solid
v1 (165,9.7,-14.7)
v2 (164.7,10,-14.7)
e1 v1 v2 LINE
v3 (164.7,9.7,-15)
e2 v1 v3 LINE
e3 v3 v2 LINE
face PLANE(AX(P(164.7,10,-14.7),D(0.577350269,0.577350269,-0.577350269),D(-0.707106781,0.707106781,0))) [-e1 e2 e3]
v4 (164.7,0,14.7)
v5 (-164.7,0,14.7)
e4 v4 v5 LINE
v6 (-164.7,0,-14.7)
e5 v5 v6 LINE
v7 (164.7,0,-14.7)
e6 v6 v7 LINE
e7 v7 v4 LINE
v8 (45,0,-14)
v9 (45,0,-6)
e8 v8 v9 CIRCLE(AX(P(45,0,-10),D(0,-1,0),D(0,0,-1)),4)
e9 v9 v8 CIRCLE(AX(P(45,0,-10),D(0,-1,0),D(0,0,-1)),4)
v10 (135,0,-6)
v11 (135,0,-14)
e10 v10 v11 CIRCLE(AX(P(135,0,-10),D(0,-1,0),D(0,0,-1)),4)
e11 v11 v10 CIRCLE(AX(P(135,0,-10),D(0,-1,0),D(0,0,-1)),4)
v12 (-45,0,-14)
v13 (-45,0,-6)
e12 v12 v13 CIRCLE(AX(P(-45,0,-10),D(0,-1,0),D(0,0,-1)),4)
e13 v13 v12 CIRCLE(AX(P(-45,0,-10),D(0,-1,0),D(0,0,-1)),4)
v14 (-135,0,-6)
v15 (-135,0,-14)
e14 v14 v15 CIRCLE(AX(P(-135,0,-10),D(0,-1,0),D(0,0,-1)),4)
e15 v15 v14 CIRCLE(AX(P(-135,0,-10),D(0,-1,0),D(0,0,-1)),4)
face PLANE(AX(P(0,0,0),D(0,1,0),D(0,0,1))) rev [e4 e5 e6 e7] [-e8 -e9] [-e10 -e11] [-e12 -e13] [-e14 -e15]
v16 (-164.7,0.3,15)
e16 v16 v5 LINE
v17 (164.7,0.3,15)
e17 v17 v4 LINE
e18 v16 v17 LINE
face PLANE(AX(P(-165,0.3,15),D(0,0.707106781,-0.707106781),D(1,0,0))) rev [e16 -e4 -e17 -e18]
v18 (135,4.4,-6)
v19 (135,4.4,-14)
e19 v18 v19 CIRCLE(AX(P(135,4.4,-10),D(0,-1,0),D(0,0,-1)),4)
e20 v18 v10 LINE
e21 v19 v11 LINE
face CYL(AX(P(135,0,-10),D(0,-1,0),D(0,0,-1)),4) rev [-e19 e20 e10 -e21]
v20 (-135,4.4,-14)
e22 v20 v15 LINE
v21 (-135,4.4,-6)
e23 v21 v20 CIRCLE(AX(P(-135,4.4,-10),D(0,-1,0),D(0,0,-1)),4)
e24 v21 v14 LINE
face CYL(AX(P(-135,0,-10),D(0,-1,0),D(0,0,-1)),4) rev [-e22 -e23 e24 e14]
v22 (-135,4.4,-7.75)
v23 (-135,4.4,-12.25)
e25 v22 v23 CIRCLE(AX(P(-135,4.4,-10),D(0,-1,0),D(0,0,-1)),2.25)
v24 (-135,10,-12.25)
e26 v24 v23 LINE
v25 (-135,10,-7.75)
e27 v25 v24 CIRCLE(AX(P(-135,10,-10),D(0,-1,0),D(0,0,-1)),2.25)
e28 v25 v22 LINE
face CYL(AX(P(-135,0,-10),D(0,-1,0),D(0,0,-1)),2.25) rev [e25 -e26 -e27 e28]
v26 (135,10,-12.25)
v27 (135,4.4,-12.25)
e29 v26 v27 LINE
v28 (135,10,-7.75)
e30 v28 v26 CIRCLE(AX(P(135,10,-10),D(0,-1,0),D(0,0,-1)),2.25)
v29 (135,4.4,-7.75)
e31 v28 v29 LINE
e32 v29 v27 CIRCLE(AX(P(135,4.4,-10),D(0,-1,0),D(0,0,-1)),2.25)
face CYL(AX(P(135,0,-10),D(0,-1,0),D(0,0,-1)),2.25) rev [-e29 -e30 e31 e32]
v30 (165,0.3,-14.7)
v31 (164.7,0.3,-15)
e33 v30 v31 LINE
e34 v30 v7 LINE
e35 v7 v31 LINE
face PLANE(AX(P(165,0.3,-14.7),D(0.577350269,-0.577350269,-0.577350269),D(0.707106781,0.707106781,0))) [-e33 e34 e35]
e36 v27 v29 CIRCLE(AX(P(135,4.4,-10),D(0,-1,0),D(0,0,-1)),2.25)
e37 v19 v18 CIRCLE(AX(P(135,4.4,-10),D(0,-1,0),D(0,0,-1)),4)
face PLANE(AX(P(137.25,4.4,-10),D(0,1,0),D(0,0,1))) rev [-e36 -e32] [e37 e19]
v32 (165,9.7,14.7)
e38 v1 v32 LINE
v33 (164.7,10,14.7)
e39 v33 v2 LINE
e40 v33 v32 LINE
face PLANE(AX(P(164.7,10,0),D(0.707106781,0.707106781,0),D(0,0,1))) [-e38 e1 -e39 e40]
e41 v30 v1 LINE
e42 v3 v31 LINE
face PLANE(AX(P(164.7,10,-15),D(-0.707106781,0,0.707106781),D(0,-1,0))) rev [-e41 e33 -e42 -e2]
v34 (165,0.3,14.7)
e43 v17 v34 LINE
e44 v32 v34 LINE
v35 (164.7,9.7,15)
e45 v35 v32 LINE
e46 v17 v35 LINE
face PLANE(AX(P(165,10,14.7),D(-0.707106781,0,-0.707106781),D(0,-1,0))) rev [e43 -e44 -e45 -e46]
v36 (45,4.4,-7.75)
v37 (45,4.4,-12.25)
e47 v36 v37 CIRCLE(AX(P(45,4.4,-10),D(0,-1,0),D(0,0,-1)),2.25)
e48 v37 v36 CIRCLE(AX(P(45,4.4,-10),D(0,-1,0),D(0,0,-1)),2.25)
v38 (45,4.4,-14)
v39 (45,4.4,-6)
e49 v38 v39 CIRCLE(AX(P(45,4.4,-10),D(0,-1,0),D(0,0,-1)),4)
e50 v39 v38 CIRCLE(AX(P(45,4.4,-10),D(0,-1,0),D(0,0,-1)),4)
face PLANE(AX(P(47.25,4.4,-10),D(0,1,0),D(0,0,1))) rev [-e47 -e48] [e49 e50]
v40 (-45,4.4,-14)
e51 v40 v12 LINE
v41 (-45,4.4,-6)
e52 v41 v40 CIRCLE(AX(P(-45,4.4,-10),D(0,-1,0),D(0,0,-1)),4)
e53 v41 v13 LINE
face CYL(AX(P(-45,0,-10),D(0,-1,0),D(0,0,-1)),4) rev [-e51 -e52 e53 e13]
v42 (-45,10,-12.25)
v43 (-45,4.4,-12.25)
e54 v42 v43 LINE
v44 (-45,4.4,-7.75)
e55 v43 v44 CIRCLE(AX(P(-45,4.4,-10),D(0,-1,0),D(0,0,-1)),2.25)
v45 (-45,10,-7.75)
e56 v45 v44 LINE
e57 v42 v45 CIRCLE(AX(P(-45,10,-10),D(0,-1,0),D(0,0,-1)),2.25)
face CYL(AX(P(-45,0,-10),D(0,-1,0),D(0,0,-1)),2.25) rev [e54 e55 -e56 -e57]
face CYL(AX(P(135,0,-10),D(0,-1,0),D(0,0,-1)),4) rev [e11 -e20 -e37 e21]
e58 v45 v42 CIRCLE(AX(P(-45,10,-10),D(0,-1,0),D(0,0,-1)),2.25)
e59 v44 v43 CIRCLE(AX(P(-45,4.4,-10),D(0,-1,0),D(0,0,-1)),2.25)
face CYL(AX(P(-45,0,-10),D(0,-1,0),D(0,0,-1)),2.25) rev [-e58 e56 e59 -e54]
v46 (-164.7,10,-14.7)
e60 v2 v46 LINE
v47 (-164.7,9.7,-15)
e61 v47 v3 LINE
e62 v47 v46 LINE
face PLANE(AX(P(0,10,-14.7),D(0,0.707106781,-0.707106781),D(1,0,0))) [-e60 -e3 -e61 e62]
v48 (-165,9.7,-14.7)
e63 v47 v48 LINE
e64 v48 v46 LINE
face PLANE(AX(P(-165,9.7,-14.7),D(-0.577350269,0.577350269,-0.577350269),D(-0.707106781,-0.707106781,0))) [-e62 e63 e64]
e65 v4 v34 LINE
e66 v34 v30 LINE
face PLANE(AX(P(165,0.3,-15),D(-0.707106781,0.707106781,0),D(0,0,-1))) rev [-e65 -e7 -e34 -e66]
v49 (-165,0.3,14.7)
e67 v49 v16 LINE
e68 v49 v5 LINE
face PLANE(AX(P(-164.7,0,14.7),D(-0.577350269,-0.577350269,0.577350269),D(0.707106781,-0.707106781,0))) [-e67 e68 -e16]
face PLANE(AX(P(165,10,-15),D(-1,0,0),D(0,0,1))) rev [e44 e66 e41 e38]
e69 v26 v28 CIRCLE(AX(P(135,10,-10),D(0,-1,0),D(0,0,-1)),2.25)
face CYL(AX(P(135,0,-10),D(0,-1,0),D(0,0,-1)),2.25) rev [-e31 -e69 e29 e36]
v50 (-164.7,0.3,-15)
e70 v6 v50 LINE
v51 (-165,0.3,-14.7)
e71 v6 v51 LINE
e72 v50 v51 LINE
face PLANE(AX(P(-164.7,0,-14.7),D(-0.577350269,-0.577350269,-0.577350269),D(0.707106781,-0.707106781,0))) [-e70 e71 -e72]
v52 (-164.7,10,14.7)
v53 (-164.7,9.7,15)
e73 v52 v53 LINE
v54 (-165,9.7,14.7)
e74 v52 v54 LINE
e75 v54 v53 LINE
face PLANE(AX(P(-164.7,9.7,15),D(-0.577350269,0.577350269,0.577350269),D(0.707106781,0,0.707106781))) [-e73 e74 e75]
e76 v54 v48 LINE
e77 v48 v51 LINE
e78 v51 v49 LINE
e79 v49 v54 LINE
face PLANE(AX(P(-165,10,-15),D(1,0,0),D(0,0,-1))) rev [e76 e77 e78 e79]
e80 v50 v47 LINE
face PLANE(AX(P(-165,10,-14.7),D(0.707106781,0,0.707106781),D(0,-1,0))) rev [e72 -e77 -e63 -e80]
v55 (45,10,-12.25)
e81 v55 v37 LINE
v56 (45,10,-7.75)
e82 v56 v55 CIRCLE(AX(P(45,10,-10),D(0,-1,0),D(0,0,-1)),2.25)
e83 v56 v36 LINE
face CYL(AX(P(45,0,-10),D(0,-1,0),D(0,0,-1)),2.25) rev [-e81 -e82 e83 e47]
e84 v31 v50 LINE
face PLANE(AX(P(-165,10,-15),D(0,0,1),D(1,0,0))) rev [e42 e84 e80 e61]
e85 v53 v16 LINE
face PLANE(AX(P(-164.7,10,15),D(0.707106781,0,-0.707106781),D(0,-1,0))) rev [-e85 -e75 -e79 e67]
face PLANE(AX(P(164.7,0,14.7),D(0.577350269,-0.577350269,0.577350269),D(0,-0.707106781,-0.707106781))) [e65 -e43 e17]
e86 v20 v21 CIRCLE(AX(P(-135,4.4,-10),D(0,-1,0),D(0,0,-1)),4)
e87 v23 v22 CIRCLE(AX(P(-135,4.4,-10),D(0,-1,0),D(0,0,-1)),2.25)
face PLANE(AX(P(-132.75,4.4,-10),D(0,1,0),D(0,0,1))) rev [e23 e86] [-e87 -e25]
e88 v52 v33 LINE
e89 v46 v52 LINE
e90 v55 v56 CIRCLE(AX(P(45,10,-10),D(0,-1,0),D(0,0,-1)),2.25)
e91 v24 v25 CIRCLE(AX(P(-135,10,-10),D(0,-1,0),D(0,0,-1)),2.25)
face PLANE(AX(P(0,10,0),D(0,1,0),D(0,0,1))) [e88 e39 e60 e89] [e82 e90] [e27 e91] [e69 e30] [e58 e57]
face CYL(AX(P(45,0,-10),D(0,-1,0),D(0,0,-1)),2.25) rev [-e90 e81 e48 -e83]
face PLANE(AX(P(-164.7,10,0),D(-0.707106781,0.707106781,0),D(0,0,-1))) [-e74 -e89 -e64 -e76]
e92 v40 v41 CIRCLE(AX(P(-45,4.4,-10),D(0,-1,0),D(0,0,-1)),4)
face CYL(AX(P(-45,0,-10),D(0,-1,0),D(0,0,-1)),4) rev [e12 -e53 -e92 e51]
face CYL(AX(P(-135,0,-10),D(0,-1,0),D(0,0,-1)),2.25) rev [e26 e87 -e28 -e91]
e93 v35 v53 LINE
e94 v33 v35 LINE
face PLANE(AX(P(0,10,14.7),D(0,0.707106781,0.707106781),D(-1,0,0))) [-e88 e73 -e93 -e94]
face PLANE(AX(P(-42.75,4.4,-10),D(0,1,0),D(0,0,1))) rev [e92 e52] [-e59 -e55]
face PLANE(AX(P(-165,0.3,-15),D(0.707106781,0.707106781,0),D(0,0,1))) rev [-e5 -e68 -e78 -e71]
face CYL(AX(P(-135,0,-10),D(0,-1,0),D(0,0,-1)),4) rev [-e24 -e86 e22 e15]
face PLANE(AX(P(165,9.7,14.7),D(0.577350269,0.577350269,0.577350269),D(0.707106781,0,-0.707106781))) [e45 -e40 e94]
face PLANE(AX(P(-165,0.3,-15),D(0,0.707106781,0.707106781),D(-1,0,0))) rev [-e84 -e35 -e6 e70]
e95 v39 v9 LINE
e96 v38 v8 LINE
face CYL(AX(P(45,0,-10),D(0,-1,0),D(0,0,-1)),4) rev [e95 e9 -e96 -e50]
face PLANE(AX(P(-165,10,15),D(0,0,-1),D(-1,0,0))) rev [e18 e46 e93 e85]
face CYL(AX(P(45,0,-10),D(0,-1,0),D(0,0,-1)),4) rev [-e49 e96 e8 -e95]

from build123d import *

# Parameters (mm, degrees)
SKETCH_1_W                   = 330
SKETCH_1_H                   = 30
EXTRUDE_1_DEPTH              = 10
HOLE_WIZARD_M4_1_D           = 4.5
HOLE_WIZARD_M4_1_CBORE_D     = 8
HOLE_WIZARD_M4_1_CBORE_DEPTH = 4.4
CHAMFER_1_SIZE               = 0.3


with BuildPart() as part:
    # 草图1 → 凸台-拉伸1 (new body)
    with BuildSketch(Plane(origin=(0, 0, 0), x_dir=(1, 0, 0), z_dir=(0, 1, 0))):
        Rectangle(SKETCH_1_W, SKETCH_1_H)
    extrude(amount=EXTRUDE_1_DEPTH)

    # M4 六角凹头螺钉的柱形沉头孔1 (through all)
    with Locations(Plane(origin=(0, 0, 0), x_dir=(-1, 0, 0), z_dir=(0, -1, 0))):
        with Locations((-135, 10), (-45, 10), (45, 10), (135, 10)):
            CounterBoreHole(HOLE_WIZARD_M4_1_D / 2, HOLE_WIZARD_M4_1_CBORE_D / 2, HOLE_WIZARD_M4_1_CBORE_DEPTH)

    # 倒角1
    chamfer_1_edges = [part.edges().sort_by_distance(p)[0] for p in [
        (-165, 10, 0),
        (0, 10, 15),
        (165, 10, 0),
        (0, 0, 15),
        (-165, 0, 0),
        (0, 0, -15),
        (165, 0, 0),
        (0, 10, -15),
        (165, 5, 15),
        (-165, 5, 15),
        (-165, 5, -15),
        (165, 5, -15),
    ]]
    chamfer(chamfer_1_edges, length=CHAMFER_1_SIZE)


solid = part.part
